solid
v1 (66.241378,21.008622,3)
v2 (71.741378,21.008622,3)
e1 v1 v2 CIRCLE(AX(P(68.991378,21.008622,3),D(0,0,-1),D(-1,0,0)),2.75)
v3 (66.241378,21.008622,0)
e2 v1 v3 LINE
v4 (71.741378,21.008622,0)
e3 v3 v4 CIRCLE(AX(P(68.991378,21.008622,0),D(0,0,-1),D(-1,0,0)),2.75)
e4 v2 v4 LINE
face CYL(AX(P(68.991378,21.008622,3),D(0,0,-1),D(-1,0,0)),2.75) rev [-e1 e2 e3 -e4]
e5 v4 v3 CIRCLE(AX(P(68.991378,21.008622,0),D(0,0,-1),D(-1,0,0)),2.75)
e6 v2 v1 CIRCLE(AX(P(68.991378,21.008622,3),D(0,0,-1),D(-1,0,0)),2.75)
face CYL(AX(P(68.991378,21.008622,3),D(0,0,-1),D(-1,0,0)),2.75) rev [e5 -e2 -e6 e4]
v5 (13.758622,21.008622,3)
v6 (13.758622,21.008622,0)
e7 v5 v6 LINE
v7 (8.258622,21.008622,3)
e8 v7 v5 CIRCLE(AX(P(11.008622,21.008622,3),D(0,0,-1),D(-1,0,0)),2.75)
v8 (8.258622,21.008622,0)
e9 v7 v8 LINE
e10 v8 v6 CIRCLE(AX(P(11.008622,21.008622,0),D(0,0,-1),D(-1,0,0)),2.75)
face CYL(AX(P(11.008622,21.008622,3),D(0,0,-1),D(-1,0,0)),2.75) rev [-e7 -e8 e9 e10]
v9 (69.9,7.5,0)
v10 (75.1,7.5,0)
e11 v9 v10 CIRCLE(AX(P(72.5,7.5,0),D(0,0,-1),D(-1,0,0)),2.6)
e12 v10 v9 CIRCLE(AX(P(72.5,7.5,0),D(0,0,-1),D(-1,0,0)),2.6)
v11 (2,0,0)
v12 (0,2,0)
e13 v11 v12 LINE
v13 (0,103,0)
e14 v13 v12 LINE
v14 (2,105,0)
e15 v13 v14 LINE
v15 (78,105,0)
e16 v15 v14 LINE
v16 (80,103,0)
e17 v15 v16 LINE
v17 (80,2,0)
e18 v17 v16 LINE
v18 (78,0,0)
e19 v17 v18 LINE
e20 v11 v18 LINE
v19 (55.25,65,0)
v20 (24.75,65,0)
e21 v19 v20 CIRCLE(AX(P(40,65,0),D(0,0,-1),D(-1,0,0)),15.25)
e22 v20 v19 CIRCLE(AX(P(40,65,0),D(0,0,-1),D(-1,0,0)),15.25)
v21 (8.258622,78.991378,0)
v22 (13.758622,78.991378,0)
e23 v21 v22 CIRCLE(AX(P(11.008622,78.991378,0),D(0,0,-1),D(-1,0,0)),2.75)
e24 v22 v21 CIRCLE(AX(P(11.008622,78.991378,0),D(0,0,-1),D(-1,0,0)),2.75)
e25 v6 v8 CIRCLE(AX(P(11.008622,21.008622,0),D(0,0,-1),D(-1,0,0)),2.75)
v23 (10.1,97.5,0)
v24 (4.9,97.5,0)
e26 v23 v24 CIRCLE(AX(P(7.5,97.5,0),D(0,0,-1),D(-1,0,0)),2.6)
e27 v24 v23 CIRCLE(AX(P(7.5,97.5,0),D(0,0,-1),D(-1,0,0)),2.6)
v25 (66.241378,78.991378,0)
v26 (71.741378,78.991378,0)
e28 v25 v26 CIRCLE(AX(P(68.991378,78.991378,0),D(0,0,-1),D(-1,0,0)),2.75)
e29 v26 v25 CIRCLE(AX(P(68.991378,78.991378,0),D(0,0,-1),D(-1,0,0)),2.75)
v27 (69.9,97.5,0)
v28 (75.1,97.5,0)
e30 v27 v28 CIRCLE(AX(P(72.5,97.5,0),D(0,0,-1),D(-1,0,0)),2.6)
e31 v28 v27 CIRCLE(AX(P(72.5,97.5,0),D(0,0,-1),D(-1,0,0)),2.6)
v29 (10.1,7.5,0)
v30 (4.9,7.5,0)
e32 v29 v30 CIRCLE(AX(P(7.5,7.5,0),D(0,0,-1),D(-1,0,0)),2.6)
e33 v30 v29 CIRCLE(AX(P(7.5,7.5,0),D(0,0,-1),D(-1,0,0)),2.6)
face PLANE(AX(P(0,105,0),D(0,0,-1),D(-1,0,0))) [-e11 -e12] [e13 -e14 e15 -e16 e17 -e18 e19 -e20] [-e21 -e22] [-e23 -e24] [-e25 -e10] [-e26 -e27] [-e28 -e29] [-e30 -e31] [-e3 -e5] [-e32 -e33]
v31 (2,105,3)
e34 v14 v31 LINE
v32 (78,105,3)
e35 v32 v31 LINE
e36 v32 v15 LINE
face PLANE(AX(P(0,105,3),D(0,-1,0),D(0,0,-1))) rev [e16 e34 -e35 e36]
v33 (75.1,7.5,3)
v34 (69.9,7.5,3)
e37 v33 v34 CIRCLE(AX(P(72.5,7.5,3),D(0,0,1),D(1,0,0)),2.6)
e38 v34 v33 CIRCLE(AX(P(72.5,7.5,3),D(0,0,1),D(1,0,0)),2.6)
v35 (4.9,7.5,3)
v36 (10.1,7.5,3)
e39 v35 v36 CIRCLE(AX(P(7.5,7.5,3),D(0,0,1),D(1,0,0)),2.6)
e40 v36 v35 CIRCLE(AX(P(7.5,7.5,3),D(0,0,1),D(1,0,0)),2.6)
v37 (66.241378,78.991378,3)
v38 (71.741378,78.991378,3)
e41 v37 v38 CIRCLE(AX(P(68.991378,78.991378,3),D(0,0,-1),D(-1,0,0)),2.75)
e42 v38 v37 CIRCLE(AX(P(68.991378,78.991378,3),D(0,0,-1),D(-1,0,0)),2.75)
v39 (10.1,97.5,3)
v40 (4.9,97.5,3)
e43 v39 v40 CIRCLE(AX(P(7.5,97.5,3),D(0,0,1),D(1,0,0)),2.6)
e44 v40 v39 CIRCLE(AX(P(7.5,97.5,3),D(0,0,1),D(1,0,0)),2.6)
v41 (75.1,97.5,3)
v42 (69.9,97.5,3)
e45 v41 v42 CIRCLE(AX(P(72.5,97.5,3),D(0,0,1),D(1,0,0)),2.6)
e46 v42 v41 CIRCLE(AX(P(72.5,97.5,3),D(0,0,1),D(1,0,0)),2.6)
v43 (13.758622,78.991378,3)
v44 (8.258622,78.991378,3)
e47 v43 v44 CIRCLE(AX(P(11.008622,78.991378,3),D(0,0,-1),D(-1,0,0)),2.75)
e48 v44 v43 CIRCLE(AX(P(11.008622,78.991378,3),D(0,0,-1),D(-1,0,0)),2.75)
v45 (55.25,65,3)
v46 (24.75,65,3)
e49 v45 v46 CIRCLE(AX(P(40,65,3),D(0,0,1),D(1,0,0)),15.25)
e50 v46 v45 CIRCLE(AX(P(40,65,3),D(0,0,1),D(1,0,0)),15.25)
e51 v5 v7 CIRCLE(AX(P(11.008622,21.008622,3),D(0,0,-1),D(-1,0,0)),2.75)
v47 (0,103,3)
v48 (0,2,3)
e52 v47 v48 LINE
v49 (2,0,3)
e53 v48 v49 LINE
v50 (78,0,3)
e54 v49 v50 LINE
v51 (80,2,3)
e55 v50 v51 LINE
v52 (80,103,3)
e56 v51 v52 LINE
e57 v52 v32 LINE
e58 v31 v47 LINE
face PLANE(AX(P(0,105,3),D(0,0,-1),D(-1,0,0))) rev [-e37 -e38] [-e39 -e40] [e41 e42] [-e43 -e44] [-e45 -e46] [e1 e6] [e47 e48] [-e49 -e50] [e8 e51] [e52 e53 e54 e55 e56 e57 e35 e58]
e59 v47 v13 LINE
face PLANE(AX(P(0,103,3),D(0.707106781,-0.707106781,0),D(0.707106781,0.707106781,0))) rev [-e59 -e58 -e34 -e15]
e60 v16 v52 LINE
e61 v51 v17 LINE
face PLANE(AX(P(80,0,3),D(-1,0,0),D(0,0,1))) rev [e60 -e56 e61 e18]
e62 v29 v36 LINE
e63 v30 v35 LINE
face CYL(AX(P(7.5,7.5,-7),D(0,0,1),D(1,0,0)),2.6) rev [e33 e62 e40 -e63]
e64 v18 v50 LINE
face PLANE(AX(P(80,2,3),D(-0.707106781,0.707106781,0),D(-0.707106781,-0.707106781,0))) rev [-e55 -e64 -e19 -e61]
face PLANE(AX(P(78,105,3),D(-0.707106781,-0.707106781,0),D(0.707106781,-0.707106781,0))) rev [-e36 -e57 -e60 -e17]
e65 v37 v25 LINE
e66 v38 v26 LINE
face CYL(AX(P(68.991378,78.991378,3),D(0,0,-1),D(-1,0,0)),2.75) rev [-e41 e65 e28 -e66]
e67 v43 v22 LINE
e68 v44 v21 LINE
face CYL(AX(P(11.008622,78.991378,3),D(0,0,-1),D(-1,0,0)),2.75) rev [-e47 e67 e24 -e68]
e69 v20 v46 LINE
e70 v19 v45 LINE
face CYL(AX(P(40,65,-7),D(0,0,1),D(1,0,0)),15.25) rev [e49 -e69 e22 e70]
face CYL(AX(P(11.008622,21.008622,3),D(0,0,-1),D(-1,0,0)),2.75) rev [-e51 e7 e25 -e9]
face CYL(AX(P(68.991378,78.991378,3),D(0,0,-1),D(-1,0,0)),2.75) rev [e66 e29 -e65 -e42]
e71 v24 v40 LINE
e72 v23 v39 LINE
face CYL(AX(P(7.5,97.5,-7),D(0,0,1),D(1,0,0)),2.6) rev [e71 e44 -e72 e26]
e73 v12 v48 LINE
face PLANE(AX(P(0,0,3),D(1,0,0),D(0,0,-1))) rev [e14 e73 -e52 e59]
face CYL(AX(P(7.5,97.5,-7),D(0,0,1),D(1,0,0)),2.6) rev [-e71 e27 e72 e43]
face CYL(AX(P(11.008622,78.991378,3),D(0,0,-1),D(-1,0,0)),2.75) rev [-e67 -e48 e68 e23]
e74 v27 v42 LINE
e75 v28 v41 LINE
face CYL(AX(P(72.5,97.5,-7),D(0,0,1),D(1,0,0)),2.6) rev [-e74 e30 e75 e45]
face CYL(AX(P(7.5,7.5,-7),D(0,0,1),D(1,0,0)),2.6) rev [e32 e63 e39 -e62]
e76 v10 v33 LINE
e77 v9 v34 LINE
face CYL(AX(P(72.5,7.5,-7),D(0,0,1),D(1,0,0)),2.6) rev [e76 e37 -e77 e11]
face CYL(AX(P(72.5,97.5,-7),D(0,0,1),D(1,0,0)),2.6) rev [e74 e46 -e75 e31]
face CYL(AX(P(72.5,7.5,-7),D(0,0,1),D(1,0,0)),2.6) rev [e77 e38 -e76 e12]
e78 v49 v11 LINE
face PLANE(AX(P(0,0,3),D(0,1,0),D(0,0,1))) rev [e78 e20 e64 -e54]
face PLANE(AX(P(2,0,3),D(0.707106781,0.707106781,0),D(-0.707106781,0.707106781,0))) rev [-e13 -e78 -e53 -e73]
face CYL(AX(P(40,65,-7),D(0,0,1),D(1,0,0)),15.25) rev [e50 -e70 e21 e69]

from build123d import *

# Parameters (mm, degrees)
SKETCH1_W             = 80
SKETCH1_H             = 105
BOSS_EXTRUDE1_DEPTH   = 3
SKETCH2_R             = 2.6
SKETCH2_R_2           = 15.25
CUT_EXTRUDE1_DEPTH    = 10
M5_TAPPED_HOLE1_D     = 4.2
M5_TAPPED_HOLE1_DEPTH = 12.4
M5_TAPPED_HOLE1_TIP   = 1.2618073
CHAMFER1_SIZE         = 2
SKETCH6_R             = 2.75
CUT_EXTRUDE3_DEPTH    = 133.037873355


with BuildPart() as part:
    # Sketch1 → Boss-Extrude1 (new body)
    with BuildSketch(Plane.XY):
        with Locations((40, 52.5)):
            Rectangle(SKETCH1_W, SKETCH1_H)
    extrude(amount=BOSS_EXTRUDE1_DEPTH)

    # Sketch2 → Cut-Extrude1 (cut)
    with BuildSketch(Plane.XY.offset(3)):
        with Locations((7.5, 97.5)):
            Circle(SKETCH2_R)
        with Locations((72.5, 97.5)):
            Circle(SKETCH2_R)
        with Locations((7.5, 7.5)):
            Circle(SKETCH2_R)
        with Locations((72.5, 7.5)):
            Circle(SKETCH2_R)
        with Locations((40, 65)):
            Circle(SKETCH2_R_2)
    extrude(amount=-CUT_EXTRUDE1_DEPTH, mode=Mode.SUBTRACT)

    # M5 Tapped Hole1
    with Locations(Plane.XY.offset(3)):
        with Locations((11.008621971, 78.991378029), (68.991378029, 78.991378029), (11.008621971, 21.008621971), (68.991378029, 21.008621971)):
            Hole(M5_TAPPED_HOLE1_D / 2, depth=M5_TAPPED_HOLE1_DEPTH)
            with Locations((0, 0, -(M5_TAPPED_HOLE1_DEPTH + M5_TAPPED_HOLE1_TIP / 2))):  # 118° drill point
                Cone(0, M5_TAPPED_HOLE1_D / 2, M5_TAPPED_HOLE1_TIP, mode=Mode.SUBTRACT)

    # Chamfer1
    chamfer1_edges = [part.edges().sort_by_distance(p)[0] for p in [
        (0, 105, 1.5),
        (80, 105, 1.5),
        (80, 0, 1.5),
        (0, 0, 1.5),
    ]]
    chamfer(chamfer1_edges, length=CHAMFER1_SIZE)

    # Sketch6 → Cut-Extrude3 (cut, through all)
    with BuildSketch(Plane(origin=(0, 0, 0), x_dir=(-1, 0, 0), z_dir=(0, 0, -1))):
        with Locations((-68.991378029, 78.991378029)):
            Circle(SKETCH6_R)
        with Locations((-11.008621971, 78.991378029)):
            Circle(SKETCH6_R)
        with Locations((-68.991378029, 21.008621971)):
            Circle(SKETCH6_R)
        with Locations((-11.008621971, 21.008621971)):
            Circle(SKETCH6_R)
    extrude(amount=-CUT_EXTRUDE3_DEPTH, mode=Mode.SUBTRACT)


solid = part.part
